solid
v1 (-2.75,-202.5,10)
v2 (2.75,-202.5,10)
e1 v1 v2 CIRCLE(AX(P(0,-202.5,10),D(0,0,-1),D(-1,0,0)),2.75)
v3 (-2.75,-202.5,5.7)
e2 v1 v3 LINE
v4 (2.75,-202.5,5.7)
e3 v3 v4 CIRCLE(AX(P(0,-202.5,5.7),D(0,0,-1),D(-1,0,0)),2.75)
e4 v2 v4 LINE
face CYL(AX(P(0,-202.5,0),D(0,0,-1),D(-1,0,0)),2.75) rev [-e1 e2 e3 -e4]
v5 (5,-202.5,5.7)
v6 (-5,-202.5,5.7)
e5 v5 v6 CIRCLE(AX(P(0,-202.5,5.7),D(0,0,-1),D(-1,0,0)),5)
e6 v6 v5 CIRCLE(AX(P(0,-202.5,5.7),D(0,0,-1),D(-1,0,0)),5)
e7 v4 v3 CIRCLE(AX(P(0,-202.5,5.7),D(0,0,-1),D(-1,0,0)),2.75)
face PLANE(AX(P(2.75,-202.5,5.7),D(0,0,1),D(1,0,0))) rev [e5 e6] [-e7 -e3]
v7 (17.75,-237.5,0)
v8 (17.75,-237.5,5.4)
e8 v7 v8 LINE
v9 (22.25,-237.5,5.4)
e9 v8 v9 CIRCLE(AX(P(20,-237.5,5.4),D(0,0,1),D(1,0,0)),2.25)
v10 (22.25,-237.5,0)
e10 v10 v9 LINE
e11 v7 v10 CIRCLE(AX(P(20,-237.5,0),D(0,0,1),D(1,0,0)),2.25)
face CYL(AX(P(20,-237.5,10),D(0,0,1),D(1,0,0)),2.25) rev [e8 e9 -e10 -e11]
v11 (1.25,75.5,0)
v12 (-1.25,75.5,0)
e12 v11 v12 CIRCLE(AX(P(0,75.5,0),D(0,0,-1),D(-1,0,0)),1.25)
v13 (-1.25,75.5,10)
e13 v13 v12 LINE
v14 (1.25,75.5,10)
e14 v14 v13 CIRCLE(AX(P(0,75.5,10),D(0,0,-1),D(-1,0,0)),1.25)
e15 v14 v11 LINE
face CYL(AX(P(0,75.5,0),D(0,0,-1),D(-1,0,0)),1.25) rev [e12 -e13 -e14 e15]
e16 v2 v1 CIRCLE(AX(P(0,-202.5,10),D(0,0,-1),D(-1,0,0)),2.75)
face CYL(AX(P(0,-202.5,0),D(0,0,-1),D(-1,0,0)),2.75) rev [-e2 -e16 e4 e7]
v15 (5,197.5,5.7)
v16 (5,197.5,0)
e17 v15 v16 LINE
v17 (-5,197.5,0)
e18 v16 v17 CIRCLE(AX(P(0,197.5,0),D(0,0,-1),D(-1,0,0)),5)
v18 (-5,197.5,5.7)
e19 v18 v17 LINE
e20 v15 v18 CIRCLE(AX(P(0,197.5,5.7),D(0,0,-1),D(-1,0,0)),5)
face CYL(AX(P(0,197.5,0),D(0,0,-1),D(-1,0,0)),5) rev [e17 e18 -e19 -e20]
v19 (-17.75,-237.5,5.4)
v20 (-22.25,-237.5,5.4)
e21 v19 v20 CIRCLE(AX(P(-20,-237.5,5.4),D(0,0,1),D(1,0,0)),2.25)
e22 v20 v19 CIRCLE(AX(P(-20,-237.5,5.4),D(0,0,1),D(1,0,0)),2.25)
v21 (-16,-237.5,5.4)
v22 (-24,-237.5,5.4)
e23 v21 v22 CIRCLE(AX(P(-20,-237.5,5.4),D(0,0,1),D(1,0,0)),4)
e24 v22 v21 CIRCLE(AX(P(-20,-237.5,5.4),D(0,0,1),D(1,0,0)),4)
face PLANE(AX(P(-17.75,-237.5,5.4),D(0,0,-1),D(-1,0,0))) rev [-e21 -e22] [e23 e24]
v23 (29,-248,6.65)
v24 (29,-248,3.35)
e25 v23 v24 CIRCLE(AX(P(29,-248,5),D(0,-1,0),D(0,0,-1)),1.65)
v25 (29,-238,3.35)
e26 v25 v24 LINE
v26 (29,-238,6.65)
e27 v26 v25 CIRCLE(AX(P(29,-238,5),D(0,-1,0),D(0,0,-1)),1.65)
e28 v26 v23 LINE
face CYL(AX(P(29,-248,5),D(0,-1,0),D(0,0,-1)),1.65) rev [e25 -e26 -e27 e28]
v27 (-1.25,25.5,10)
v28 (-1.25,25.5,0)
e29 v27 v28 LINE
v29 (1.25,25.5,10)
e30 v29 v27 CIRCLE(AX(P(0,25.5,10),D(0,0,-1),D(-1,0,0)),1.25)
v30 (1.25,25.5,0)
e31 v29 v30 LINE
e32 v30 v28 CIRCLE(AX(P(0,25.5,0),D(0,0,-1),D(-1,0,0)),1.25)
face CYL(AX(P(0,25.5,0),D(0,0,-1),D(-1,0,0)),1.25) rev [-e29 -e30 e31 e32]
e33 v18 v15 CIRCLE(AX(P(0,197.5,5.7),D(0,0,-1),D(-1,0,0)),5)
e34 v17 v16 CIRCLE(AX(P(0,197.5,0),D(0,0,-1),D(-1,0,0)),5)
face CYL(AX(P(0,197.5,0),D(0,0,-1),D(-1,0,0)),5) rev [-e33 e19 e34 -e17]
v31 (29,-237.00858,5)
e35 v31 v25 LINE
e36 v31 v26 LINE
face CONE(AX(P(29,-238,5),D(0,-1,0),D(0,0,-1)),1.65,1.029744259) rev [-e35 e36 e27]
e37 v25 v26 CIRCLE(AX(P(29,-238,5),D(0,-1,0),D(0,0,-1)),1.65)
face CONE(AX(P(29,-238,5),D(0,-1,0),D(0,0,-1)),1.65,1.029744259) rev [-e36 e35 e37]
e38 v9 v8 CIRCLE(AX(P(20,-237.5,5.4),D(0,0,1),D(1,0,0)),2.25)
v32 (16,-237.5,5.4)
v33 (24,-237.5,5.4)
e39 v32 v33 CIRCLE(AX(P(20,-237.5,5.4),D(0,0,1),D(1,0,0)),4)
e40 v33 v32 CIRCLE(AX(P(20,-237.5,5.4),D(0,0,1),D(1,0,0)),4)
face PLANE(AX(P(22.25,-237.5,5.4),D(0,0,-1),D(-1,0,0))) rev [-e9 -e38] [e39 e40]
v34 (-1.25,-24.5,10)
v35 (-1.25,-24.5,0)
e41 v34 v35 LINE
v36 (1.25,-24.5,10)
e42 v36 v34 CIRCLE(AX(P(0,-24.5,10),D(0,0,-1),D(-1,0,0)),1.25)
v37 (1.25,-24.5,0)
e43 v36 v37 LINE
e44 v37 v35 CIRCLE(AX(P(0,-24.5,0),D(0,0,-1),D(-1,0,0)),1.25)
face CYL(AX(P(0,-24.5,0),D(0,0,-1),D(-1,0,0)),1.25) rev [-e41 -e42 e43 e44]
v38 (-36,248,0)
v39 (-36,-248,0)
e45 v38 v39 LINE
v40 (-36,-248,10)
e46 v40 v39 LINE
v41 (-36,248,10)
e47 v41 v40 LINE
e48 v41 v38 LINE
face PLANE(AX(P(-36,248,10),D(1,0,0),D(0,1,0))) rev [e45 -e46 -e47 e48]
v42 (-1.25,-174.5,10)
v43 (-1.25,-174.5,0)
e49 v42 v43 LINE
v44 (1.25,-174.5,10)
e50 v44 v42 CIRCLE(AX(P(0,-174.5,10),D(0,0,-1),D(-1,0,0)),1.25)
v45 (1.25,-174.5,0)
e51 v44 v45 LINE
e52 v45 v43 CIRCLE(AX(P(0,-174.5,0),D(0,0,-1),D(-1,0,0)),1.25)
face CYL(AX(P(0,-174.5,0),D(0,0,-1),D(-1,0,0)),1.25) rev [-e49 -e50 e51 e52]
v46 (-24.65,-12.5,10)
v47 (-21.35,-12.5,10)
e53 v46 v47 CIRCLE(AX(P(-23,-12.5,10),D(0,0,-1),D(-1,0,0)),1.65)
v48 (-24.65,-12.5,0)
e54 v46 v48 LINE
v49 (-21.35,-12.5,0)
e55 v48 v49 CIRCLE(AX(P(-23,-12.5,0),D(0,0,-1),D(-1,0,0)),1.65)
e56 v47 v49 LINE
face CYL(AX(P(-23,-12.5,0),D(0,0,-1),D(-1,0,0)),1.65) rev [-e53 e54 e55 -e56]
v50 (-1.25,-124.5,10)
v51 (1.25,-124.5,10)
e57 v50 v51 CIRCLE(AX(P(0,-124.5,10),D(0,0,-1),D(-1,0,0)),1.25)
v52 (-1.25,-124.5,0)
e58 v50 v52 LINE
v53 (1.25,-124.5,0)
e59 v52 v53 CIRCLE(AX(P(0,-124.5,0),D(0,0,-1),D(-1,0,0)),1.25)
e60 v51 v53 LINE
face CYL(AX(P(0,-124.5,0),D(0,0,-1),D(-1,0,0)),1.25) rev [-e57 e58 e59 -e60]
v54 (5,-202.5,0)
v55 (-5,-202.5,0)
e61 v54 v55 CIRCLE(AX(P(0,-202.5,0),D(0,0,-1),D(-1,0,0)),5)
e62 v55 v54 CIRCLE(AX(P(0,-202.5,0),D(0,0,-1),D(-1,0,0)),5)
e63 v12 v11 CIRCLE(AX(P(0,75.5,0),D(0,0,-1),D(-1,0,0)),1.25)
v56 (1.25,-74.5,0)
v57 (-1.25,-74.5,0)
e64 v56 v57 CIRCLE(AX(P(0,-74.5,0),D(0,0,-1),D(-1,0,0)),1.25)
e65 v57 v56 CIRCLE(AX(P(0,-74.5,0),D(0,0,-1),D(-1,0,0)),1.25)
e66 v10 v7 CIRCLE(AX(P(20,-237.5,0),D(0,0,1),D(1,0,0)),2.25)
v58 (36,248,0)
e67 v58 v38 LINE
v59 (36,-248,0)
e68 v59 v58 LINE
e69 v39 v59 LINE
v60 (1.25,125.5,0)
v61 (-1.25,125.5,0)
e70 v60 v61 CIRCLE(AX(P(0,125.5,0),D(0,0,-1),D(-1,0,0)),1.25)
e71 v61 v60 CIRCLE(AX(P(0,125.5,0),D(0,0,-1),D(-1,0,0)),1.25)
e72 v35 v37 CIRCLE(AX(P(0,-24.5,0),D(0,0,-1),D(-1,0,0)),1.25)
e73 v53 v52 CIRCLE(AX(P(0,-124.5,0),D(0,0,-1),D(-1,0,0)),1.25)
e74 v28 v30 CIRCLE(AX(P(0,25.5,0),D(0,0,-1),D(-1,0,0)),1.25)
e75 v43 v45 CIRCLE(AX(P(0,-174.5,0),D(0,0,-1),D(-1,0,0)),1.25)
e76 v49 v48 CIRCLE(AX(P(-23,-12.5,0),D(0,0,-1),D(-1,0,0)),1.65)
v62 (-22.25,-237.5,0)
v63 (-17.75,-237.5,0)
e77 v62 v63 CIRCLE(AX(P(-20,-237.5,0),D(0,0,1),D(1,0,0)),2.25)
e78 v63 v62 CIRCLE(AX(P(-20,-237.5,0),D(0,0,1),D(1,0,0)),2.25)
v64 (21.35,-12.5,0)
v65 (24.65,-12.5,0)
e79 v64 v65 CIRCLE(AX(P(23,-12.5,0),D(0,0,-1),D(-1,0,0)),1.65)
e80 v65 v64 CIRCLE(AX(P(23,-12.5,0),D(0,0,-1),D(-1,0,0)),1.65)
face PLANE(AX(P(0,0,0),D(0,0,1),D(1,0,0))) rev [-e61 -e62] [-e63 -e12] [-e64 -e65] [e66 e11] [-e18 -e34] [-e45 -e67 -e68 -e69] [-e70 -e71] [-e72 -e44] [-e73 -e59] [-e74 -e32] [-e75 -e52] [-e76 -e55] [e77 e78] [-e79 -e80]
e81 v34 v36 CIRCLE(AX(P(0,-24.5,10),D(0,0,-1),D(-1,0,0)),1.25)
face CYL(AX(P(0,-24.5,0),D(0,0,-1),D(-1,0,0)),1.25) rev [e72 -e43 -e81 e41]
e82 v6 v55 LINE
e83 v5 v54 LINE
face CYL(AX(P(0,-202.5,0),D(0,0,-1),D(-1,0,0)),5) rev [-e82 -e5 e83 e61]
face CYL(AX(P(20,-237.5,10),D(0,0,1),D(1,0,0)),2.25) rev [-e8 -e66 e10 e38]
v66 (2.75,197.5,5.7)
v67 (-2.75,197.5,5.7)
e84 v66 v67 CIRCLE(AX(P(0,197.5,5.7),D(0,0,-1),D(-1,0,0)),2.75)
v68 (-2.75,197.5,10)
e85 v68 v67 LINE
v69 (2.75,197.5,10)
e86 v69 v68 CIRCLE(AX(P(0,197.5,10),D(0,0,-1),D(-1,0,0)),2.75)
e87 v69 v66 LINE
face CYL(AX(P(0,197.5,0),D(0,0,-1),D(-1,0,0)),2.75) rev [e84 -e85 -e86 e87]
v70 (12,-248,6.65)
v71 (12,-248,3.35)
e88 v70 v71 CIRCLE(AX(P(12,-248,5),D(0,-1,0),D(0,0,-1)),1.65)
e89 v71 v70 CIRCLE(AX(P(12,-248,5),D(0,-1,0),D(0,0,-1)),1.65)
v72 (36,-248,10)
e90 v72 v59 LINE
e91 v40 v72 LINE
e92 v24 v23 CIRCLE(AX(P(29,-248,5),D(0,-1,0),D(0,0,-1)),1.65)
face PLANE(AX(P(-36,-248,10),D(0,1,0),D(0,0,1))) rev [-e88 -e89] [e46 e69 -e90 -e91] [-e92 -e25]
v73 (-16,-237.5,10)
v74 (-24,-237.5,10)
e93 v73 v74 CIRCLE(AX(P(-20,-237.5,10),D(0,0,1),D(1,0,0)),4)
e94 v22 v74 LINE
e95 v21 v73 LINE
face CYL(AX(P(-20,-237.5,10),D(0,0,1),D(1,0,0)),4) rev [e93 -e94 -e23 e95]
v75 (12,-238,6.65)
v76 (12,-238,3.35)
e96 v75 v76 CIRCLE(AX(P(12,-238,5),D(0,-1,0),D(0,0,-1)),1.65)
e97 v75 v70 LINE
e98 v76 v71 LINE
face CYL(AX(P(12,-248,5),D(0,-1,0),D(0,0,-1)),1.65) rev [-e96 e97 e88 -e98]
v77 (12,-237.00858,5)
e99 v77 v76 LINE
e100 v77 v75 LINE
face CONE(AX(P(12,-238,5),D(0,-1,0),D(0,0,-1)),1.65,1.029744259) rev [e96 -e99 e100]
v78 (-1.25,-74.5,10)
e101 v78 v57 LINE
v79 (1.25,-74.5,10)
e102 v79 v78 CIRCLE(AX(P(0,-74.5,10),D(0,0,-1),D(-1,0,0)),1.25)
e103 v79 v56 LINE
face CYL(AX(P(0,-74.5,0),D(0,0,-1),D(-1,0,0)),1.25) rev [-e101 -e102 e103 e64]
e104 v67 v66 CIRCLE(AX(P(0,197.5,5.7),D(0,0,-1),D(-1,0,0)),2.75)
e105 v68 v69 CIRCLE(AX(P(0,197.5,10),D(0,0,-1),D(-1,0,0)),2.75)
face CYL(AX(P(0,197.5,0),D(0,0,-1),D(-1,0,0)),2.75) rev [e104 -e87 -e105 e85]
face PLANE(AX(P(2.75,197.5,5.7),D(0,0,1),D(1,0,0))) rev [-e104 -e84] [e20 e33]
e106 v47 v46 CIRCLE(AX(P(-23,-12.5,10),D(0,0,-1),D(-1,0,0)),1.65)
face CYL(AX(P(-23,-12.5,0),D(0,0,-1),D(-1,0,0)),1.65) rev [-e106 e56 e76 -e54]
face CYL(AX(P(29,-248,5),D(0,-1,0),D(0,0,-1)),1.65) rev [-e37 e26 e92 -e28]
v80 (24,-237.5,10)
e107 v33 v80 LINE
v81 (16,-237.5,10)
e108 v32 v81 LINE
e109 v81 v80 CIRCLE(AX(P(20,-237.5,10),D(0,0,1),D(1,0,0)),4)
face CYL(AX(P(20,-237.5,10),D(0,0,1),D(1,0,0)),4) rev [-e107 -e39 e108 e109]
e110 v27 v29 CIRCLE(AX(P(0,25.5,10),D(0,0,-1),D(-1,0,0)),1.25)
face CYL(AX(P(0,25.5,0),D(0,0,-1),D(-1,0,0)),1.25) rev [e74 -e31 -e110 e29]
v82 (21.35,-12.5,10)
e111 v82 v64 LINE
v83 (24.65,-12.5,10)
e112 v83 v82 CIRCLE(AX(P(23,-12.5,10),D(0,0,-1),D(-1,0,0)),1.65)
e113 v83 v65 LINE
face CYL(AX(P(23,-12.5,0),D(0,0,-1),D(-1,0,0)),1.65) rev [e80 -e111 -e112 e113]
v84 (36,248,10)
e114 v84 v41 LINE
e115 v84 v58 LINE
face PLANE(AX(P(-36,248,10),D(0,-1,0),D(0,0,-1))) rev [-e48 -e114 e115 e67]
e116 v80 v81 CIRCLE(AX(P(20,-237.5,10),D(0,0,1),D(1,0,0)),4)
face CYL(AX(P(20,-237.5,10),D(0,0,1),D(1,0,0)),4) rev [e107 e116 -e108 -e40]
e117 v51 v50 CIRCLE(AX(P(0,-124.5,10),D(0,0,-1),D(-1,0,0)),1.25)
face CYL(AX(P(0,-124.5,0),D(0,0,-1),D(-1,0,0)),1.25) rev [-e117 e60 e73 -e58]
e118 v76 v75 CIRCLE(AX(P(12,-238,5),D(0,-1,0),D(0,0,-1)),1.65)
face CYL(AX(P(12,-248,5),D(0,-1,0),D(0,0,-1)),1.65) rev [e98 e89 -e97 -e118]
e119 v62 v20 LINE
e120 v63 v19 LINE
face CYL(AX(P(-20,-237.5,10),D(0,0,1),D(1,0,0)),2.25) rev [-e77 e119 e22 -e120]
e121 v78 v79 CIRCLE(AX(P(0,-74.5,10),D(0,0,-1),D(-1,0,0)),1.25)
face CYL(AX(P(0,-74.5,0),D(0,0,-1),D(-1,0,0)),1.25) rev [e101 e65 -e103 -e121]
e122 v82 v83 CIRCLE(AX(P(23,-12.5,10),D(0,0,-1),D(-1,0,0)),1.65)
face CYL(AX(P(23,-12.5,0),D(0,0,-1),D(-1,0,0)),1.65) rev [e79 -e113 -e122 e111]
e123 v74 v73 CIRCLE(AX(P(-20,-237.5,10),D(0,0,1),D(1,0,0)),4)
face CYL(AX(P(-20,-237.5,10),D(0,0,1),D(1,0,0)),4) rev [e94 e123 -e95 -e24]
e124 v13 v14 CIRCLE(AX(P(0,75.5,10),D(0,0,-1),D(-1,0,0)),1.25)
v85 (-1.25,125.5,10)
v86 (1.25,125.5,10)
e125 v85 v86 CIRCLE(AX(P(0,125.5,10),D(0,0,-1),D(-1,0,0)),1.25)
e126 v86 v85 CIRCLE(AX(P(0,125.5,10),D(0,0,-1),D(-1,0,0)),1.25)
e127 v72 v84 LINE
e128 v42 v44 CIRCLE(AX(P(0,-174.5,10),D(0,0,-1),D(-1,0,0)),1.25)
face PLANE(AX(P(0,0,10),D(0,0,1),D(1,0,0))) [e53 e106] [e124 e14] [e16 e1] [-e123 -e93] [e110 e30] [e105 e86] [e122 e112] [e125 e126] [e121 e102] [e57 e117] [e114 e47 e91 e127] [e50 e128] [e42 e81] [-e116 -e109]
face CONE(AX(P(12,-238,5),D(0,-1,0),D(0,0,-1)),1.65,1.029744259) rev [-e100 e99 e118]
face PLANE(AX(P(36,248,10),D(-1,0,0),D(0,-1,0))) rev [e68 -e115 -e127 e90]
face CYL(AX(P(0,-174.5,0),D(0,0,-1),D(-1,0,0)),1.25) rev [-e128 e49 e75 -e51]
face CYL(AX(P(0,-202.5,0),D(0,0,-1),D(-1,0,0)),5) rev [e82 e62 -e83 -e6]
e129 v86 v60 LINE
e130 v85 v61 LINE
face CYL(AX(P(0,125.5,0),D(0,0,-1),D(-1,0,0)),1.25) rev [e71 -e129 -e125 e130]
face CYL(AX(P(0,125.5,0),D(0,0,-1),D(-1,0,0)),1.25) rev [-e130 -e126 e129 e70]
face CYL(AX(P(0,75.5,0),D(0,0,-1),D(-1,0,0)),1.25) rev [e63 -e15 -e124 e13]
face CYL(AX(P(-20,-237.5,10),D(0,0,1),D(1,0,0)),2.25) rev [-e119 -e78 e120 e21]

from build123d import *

# Parameters (mm, degrees)
SKETCH_1_W                = 72
SKETCH_1_H                = 496
EXTRUDE_1_DEPTH           = 10
HOLE_WIZARD_2_D           = 5.5
HOLE_WIZARD_2_CBORE_D     = 10
HOLE_WIZARD_2_CBORE_DEPTH = 5.7
HOLE_WIZARD_0_D           = 4.5
HOLE_WIZARD_0_CBORE_D     = 8
HOLE_WIZARD_0_CBORE_DEPTH = 4.6
HOLE_WIZARD_M4_2_D        = 3.3
HOLE_WIZARD_M4_2_DEPTH    = 10
HOLE_WIZARD_M4_2_TIP      = 0.991420021
HOLE_WIZARD_M4_3_D        = 3.3
HOLE_WIZARD_M3_1_D        = 2.5


with BuildPart() as part:
    # 草图1 → 凸台-拉伸1 (new body)
    with BuildSketch(Plane.XY):
        Rectangle(SKETCH_1_W, SKETCH_1_H)
    extrude(amount=EXTRUDE_1_DEPTH)

    # 打孔尺寸根据内六角圆柱头螺钉的类型2 (through all)
    with Locations(Plane(origin=(0, 0, 0), x_dir=(-1, 0, 0), z_dir=(0, 0, -1))):
        with Locations((0, -202.499999994), (0, 197.500000006)):
            CounterBoreHole(HOLE_WIZARD_2_D / 2, HOLE_WIZARD_2_CBORE_D / 2, HOLE_WIZARD_2_CBORE_DEPTH)

    # 打孔尺寸根据内六角圆柱头螺钉的类型0 (through all)
    with Locations(Plane.XY.offset(10)):
        with Locations((-20, -237.5), (20, -237.5)):
            CounterBoreHole(HOLE_WIZARD_0_D / 2, HOLE_WIZARD_0_CBORE_D / 2, HOLE_WIZARD_0_CBORE_DEPTH)

    # M4 螺纹孔2
    with Locations(Plane(origin=(0, -248, 0), x_dir=(-1, 0, 0), z_dir=(0, -1, 0))):
        with Locations((-12, -5), (-29, -5)):
            Hole(HOLE_WIZARD_M4_2_D / 2, depth=HOLE_WIZARD_M4_2_DEPTH)
            with Locations((0, 0, -(HOLE_WIZARD_M4_2_DEPTH + HOLE_WIZARD_M4_2_TIP / 2))):  # 118° drill point
                Cone(0, HOLE_WIZARD_M4_2_D / 2, HOLE_WIZARD_M4_2_TIP, mode=Mode.SUBTRACT)

    # M4 螺纹孔3 (through all)
    with Locations(Plane(origin=(0, 0, 0), x_dir=(-1, 0, 0), z_dir=(0, 0, -1))):
        with Locations((-23, -12.5), (23, -12.5)):
            Hole(HOLE_WIZARD_M4_3_D / 2)

    # M3 螺纹孔1 (through all)
    with Locations(Plane(origin=(0, 0, 0), x_dir=(-1, 0, 0), z_dir=(0, 0, -1))):
        with Locations((0, -174.5), (0, -124.5), (0, -74.5), (0, -24.5), (0, 25.5), (0, 75.5), (0, 125.5)):
            Hole(HOLE_WIZARD_M3_1_D / 2)


solid = part.part
